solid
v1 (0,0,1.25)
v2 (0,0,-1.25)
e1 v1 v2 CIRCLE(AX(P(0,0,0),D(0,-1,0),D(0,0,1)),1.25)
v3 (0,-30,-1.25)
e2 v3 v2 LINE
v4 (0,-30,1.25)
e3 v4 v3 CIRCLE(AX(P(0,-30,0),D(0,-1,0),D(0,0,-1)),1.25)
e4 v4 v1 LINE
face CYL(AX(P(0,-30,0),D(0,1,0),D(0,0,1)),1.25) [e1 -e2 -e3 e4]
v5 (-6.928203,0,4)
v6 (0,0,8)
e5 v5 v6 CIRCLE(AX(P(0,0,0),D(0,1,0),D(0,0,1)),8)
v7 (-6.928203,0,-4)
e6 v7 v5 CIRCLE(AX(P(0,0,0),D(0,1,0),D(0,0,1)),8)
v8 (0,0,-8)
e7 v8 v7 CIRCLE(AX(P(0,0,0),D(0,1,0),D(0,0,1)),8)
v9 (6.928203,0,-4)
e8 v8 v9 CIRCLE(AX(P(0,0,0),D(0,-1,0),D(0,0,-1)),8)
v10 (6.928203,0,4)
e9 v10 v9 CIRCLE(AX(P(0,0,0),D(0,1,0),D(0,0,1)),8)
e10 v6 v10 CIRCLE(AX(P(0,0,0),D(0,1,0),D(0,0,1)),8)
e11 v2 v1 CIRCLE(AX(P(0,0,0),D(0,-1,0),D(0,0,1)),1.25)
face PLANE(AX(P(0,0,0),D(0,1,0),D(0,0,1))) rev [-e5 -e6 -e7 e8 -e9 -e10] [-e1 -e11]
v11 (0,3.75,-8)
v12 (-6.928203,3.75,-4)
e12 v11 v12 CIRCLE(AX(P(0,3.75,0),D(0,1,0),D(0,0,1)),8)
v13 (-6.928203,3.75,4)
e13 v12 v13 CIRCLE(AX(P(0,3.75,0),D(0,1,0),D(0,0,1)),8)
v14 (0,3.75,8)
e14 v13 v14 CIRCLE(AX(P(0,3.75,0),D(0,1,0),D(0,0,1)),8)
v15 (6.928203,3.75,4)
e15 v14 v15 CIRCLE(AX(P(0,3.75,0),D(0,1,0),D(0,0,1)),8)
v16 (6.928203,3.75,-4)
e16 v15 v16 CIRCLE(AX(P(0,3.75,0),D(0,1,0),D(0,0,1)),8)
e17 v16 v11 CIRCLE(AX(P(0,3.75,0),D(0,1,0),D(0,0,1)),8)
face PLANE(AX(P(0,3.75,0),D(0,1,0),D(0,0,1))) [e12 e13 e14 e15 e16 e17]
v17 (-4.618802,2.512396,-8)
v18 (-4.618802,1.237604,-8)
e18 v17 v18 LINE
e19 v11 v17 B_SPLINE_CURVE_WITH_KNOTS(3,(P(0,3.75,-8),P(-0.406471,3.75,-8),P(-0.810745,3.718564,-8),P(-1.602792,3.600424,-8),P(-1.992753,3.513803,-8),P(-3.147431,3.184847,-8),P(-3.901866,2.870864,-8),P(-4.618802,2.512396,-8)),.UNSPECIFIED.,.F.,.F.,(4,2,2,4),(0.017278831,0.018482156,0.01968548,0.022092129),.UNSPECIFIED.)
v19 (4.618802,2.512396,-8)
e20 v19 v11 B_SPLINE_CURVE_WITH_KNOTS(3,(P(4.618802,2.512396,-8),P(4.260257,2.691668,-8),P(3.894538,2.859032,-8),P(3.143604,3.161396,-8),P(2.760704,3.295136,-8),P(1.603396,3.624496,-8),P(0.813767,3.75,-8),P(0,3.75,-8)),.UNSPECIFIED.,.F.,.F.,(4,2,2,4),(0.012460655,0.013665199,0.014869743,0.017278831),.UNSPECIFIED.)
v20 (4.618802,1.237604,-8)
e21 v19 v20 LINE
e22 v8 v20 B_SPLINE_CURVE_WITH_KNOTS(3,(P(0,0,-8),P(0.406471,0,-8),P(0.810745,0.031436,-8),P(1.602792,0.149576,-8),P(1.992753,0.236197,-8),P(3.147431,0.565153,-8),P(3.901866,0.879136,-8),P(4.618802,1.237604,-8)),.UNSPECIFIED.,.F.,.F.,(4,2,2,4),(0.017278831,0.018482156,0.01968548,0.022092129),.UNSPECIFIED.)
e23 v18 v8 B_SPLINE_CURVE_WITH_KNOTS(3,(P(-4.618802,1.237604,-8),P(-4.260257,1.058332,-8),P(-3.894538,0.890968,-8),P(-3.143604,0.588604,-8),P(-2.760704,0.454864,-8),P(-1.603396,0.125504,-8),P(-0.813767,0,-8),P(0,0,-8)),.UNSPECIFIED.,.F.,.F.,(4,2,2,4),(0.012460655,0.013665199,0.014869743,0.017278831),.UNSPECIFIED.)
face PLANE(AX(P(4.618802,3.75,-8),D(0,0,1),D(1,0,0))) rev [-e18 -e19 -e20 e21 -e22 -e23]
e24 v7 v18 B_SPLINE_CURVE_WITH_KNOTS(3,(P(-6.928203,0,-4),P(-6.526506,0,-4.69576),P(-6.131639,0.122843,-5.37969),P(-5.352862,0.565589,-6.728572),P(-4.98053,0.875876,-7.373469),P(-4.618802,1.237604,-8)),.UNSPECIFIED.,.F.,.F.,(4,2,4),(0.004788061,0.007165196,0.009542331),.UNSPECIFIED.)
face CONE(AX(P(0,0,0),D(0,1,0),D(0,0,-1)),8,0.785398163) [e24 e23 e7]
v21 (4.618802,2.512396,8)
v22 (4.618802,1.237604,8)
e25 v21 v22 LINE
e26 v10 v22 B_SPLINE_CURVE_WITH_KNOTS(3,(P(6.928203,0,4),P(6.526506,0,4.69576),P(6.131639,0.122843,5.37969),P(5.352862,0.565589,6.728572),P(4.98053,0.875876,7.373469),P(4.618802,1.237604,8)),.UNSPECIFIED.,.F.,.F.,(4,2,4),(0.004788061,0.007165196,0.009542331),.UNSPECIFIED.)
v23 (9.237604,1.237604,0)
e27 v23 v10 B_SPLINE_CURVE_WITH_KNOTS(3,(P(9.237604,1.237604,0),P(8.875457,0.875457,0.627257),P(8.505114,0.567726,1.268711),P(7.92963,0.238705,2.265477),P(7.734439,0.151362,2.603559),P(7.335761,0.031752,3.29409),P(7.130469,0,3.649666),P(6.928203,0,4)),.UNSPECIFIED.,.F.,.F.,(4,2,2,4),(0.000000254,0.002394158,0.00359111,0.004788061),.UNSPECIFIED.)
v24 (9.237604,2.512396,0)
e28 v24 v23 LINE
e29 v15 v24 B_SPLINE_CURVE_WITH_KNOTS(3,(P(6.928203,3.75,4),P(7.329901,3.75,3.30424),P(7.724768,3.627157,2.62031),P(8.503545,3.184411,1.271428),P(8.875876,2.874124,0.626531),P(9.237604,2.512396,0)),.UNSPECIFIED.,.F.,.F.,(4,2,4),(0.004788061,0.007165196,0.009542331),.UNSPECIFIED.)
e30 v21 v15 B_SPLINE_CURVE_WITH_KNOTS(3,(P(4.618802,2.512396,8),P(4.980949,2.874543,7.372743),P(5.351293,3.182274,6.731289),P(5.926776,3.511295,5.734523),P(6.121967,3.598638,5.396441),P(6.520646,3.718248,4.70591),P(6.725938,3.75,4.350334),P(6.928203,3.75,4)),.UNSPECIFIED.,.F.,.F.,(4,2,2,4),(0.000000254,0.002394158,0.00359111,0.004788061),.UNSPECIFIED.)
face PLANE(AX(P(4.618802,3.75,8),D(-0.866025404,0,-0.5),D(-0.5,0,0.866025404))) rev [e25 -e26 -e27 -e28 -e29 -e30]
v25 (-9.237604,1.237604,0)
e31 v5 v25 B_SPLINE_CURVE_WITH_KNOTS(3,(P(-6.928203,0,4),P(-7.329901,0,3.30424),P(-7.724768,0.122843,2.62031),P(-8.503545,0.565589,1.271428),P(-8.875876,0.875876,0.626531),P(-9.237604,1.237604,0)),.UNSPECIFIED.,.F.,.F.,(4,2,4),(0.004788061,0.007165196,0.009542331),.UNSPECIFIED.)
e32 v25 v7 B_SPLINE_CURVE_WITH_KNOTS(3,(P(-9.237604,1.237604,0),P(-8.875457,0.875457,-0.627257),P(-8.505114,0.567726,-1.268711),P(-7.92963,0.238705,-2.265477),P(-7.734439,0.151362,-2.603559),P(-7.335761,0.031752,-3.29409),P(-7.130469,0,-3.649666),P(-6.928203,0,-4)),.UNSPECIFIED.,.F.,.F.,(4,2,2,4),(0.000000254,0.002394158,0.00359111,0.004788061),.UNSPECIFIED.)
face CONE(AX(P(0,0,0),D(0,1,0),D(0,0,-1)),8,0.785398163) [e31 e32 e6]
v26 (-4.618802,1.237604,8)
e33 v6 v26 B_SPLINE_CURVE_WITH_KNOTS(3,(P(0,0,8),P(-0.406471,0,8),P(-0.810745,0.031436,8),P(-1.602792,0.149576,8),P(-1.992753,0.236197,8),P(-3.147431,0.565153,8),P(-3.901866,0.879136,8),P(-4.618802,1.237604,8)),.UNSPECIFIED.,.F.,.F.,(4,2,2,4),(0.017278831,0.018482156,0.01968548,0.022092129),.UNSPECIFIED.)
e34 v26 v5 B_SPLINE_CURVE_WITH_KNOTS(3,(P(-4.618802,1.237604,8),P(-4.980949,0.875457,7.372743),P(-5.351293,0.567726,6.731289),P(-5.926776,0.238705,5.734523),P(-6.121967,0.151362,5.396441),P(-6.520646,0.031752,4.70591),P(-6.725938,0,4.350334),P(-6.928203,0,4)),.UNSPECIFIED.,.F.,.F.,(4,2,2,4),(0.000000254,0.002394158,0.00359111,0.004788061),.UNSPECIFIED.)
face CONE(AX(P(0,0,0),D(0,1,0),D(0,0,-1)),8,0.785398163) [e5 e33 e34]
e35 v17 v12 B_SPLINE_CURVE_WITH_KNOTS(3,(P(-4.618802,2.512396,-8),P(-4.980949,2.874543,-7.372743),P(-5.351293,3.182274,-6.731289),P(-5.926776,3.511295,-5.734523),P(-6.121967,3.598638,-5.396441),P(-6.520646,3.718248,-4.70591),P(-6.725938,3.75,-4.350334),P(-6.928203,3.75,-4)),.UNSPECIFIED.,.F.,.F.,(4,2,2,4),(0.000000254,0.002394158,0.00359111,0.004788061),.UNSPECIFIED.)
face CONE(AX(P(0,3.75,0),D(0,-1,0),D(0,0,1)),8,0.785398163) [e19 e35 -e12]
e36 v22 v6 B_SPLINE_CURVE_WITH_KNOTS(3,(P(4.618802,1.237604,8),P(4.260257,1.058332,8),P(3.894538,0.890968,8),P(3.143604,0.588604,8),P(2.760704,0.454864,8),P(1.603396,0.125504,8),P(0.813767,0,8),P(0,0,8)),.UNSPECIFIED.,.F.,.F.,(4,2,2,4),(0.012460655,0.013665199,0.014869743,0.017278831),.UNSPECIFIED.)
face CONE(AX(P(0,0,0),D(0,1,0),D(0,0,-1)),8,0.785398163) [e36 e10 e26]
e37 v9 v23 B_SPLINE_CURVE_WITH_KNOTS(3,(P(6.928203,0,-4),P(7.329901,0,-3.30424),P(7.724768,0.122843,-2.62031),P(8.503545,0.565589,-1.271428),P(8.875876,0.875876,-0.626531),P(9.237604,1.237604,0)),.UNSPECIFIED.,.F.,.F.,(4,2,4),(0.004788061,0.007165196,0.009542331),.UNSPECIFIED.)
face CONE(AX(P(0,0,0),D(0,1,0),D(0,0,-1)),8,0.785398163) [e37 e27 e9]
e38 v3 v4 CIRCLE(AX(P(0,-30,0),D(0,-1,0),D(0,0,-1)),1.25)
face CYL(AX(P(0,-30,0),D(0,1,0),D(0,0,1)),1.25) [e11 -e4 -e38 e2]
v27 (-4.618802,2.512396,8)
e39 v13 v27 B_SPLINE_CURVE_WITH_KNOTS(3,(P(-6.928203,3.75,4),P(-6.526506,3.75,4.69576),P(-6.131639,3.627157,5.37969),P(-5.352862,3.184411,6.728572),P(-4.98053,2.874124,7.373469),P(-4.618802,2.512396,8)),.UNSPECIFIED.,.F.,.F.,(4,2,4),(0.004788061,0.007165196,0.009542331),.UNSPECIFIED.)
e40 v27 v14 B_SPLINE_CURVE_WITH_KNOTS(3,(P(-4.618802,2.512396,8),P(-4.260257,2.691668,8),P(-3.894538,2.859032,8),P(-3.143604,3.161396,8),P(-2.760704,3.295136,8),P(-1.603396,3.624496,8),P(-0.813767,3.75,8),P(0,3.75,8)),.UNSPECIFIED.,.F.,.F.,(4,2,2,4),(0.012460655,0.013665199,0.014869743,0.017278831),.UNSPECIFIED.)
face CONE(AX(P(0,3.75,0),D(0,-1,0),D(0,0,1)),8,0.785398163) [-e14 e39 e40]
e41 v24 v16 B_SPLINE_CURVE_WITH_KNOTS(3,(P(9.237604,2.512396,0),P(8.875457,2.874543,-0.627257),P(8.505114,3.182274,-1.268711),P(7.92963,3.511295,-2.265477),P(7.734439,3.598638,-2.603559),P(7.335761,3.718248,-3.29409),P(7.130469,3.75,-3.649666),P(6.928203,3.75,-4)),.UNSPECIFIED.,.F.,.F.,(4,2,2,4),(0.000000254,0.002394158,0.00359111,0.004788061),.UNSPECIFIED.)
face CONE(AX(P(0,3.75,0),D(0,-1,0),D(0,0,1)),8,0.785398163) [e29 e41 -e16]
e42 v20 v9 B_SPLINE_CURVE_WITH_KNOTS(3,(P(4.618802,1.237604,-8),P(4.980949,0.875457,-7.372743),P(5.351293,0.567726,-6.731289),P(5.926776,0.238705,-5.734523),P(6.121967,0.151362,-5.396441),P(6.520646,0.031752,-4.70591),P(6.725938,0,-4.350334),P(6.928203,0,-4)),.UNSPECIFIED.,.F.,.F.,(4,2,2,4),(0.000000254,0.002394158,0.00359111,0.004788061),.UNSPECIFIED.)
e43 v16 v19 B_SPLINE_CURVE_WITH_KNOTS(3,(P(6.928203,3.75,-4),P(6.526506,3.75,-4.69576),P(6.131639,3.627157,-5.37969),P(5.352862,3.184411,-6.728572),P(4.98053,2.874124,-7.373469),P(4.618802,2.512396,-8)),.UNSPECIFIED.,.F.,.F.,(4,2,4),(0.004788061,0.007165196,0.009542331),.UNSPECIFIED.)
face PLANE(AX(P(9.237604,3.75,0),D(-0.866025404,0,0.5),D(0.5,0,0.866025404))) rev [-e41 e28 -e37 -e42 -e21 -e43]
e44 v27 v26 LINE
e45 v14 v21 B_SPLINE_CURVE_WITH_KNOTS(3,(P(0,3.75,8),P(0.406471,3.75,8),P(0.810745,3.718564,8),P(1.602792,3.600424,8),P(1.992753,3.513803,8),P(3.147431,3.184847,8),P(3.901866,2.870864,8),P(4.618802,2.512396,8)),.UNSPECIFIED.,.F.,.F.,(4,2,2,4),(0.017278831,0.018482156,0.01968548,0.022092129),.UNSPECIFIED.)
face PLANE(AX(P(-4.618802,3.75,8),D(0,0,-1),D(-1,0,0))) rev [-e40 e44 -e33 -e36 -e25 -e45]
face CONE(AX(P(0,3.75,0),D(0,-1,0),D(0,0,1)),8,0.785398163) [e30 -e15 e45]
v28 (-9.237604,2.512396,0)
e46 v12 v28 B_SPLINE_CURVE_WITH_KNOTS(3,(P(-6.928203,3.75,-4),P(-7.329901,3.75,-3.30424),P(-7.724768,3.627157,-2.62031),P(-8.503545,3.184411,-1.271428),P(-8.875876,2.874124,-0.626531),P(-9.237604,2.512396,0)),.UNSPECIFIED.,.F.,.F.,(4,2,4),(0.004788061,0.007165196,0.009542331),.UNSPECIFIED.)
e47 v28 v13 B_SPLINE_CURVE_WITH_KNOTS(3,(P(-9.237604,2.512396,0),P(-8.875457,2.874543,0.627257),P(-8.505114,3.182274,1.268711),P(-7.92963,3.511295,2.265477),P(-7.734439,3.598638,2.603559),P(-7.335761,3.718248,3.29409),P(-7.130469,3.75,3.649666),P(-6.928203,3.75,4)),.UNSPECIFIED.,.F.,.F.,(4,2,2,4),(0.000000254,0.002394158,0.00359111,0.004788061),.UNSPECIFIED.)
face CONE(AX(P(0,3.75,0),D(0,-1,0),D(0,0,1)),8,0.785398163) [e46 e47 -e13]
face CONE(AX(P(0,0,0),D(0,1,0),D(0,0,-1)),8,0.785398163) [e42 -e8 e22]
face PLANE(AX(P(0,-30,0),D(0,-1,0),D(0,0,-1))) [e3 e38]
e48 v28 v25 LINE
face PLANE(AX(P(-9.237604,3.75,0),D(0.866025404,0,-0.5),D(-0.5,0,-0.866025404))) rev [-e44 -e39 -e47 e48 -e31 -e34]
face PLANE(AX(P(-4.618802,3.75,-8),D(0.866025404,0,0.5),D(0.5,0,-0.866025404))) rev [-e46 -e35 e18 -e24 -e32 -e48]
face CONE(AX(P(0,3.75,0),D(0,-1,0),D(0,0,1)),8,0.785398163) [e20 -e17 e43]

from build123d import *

# Parameters (mm, degrees)
HEX_HEAD_DEPTH                   = 3.75
HEAD_CHAMFER_A_PROFILE_OUTSIDE_W = 32.922
HEAD_CHAMFER_A_PROFILE_OUTSIDE_H = 30.446
HEAD_CHAMFER_A_PROFILE_OUTSIDE_R = 8
HEAD_CHAMFER_A_45DEG_DEPTH       = 3.75
HEAD_CHAMFER_A_45DEG_DRAFT       = -45
HEAD_CHAMFER_B_PROFILE_OUTSIDE_W = 32.922
HEAD_CHAMFER_B_PROFILE_OUTSIDE_H = 30.446
HEAD_CHAMFER_B_PROFILE_OUTSIDE_R = 8
HEAD_CHAMFER_B_45DEG_DEPTH       = 3.75
HEAD_CHAMFER_B_45DEG_DRAFT       = -45
SHANK_PROFILE_2_5_R              = 1.25
SHANK_2_5X30_DEPTH               = 30


with BuildPart() as part:
    # Hex Head Profile → Hex Head (new body)
    with BuildSketch(Plane(origin=(0, 0, 0), x_dir=(1, 0, 0), z_dir=(0, 1, 0))):
        Polygon((4.618802154, -8), (9.237604307, 0), (4.618802154, 8), (-4.618802154, 8), (-9.237604307, 0), (-4.618802154, -8), align=None)
    extrude(amount=HEX_HEAD_DEPTH)


with BuildPart() as head_chamfer_a_45deg_tool:
    # Head Chamfer A Profile outside → Head Chamfer A 45deg (with draft: the straight prism first)
    with BuildSketch(Plane(origin=(0, 3.75, 0), x_dir=(1, 0, 0), z_dir=(0, 1, 0))):
        Rectangle(HEAD_CHAMFER_A_PROFILE_OUTSIDE_W, HEAD_CHAMFER_A_PROFILE_OUTSIDE_H)
        Circle(HEAD_CHAMFER_A_PROFILE_OUTSIDE_R, mode=Mode.SUBTRACT)
    extrude(amount=-HEAD_CHAMFER_A_45DEG_DEPTH)
    # Head Chamfer A 45deg: the draft: its side faces are tilted about the plane it starts from
    head_chamfer_a_45deg_sides = [head_chamfer_a_45deg_tool.faces().sort_by_distance(p)[0] for p in [
        (0, 1.875, 15.223),
        (16.461, 1.875, 0),
        (0, 1.875, -15.223),
        (-16.461, 1.875, 0),
        (-8, 1.875, 0),
    ]]
    draft(head_chamfer_a_45deg_sides, Plane(origin=(0, 3.75, 0), x_dir=(1, 0, 0), z_dir=(0, 1, 0)), HEAD_CHAMFER_A_45DEG_DRAFT)


with BuildPart() as part_1:
    add(part.part)

    # Head Chamfer A 45deg: cut by head_chamfer_a_45deg_tool
    add(head_chamfer_a_45deg_tool.part, mode=Mode.SUBTRACT)


with BuildPart() as head_chamfer_b_45deg_tool:
    # Head Chamfer B Profile outside → Head Chamfer B 45deg (with draft: the straight prism first)
    with BuildSketch(Plane.XZ):
        Rectangle(HEAD_CHAMFER_B_PROFILE_OUTSIDE_W, HEAD_CHAMFER_B_PROFILE_OUTSIDE_H)
        Circle(HEAD_CHAMFER_B_PROFILE_OUTSIDE_R, mode=Mode.SUBTRACT)
    extrude(amount=-HEAD_CHAMFER_B_45DEG_DEPTH)
    # Head Chamfer B 45deg: the draft: its side faces are tilted about the plane it starts from
    head_chamfer_b_45deg_sides = [head_chamfer_b_45deg_tool.faces().sort_by_distance(p)[0] for p in [
        (0, 1.875, -15.223),
        (16.461, 1.875, 0),
        (0, 1.875, 15.223),
        (-16.461, 1.875, 0),
        (-8, 1.875, 0),
    ]]
    draft(head_chamfer_b_45deg_sides, Plane.XZ, HEAD_CHAMFER_B_45DEG_DRAFT)


with BuildPart() as part_2:
    add(part_1.part)

    # Head Chamfer B 45deg: cut by head_chamfer_b_45deg_tool
    add(head_chamfer_b_45deg_tool.part, mode=Mode.SUBTRACT)

    # Shank Profile Ø2.5 → Shank Ø2.5x30 (add)
    with BuildSketch(Plane.XZ):
        with Locations(Location((0, 0, 0), (0, 0, 90))):
            Circle(SHANK_PROFILE_2_5_R)
    extrude(amount=SHANK_2_5X30_DEPTH)


solid = part_2.part
